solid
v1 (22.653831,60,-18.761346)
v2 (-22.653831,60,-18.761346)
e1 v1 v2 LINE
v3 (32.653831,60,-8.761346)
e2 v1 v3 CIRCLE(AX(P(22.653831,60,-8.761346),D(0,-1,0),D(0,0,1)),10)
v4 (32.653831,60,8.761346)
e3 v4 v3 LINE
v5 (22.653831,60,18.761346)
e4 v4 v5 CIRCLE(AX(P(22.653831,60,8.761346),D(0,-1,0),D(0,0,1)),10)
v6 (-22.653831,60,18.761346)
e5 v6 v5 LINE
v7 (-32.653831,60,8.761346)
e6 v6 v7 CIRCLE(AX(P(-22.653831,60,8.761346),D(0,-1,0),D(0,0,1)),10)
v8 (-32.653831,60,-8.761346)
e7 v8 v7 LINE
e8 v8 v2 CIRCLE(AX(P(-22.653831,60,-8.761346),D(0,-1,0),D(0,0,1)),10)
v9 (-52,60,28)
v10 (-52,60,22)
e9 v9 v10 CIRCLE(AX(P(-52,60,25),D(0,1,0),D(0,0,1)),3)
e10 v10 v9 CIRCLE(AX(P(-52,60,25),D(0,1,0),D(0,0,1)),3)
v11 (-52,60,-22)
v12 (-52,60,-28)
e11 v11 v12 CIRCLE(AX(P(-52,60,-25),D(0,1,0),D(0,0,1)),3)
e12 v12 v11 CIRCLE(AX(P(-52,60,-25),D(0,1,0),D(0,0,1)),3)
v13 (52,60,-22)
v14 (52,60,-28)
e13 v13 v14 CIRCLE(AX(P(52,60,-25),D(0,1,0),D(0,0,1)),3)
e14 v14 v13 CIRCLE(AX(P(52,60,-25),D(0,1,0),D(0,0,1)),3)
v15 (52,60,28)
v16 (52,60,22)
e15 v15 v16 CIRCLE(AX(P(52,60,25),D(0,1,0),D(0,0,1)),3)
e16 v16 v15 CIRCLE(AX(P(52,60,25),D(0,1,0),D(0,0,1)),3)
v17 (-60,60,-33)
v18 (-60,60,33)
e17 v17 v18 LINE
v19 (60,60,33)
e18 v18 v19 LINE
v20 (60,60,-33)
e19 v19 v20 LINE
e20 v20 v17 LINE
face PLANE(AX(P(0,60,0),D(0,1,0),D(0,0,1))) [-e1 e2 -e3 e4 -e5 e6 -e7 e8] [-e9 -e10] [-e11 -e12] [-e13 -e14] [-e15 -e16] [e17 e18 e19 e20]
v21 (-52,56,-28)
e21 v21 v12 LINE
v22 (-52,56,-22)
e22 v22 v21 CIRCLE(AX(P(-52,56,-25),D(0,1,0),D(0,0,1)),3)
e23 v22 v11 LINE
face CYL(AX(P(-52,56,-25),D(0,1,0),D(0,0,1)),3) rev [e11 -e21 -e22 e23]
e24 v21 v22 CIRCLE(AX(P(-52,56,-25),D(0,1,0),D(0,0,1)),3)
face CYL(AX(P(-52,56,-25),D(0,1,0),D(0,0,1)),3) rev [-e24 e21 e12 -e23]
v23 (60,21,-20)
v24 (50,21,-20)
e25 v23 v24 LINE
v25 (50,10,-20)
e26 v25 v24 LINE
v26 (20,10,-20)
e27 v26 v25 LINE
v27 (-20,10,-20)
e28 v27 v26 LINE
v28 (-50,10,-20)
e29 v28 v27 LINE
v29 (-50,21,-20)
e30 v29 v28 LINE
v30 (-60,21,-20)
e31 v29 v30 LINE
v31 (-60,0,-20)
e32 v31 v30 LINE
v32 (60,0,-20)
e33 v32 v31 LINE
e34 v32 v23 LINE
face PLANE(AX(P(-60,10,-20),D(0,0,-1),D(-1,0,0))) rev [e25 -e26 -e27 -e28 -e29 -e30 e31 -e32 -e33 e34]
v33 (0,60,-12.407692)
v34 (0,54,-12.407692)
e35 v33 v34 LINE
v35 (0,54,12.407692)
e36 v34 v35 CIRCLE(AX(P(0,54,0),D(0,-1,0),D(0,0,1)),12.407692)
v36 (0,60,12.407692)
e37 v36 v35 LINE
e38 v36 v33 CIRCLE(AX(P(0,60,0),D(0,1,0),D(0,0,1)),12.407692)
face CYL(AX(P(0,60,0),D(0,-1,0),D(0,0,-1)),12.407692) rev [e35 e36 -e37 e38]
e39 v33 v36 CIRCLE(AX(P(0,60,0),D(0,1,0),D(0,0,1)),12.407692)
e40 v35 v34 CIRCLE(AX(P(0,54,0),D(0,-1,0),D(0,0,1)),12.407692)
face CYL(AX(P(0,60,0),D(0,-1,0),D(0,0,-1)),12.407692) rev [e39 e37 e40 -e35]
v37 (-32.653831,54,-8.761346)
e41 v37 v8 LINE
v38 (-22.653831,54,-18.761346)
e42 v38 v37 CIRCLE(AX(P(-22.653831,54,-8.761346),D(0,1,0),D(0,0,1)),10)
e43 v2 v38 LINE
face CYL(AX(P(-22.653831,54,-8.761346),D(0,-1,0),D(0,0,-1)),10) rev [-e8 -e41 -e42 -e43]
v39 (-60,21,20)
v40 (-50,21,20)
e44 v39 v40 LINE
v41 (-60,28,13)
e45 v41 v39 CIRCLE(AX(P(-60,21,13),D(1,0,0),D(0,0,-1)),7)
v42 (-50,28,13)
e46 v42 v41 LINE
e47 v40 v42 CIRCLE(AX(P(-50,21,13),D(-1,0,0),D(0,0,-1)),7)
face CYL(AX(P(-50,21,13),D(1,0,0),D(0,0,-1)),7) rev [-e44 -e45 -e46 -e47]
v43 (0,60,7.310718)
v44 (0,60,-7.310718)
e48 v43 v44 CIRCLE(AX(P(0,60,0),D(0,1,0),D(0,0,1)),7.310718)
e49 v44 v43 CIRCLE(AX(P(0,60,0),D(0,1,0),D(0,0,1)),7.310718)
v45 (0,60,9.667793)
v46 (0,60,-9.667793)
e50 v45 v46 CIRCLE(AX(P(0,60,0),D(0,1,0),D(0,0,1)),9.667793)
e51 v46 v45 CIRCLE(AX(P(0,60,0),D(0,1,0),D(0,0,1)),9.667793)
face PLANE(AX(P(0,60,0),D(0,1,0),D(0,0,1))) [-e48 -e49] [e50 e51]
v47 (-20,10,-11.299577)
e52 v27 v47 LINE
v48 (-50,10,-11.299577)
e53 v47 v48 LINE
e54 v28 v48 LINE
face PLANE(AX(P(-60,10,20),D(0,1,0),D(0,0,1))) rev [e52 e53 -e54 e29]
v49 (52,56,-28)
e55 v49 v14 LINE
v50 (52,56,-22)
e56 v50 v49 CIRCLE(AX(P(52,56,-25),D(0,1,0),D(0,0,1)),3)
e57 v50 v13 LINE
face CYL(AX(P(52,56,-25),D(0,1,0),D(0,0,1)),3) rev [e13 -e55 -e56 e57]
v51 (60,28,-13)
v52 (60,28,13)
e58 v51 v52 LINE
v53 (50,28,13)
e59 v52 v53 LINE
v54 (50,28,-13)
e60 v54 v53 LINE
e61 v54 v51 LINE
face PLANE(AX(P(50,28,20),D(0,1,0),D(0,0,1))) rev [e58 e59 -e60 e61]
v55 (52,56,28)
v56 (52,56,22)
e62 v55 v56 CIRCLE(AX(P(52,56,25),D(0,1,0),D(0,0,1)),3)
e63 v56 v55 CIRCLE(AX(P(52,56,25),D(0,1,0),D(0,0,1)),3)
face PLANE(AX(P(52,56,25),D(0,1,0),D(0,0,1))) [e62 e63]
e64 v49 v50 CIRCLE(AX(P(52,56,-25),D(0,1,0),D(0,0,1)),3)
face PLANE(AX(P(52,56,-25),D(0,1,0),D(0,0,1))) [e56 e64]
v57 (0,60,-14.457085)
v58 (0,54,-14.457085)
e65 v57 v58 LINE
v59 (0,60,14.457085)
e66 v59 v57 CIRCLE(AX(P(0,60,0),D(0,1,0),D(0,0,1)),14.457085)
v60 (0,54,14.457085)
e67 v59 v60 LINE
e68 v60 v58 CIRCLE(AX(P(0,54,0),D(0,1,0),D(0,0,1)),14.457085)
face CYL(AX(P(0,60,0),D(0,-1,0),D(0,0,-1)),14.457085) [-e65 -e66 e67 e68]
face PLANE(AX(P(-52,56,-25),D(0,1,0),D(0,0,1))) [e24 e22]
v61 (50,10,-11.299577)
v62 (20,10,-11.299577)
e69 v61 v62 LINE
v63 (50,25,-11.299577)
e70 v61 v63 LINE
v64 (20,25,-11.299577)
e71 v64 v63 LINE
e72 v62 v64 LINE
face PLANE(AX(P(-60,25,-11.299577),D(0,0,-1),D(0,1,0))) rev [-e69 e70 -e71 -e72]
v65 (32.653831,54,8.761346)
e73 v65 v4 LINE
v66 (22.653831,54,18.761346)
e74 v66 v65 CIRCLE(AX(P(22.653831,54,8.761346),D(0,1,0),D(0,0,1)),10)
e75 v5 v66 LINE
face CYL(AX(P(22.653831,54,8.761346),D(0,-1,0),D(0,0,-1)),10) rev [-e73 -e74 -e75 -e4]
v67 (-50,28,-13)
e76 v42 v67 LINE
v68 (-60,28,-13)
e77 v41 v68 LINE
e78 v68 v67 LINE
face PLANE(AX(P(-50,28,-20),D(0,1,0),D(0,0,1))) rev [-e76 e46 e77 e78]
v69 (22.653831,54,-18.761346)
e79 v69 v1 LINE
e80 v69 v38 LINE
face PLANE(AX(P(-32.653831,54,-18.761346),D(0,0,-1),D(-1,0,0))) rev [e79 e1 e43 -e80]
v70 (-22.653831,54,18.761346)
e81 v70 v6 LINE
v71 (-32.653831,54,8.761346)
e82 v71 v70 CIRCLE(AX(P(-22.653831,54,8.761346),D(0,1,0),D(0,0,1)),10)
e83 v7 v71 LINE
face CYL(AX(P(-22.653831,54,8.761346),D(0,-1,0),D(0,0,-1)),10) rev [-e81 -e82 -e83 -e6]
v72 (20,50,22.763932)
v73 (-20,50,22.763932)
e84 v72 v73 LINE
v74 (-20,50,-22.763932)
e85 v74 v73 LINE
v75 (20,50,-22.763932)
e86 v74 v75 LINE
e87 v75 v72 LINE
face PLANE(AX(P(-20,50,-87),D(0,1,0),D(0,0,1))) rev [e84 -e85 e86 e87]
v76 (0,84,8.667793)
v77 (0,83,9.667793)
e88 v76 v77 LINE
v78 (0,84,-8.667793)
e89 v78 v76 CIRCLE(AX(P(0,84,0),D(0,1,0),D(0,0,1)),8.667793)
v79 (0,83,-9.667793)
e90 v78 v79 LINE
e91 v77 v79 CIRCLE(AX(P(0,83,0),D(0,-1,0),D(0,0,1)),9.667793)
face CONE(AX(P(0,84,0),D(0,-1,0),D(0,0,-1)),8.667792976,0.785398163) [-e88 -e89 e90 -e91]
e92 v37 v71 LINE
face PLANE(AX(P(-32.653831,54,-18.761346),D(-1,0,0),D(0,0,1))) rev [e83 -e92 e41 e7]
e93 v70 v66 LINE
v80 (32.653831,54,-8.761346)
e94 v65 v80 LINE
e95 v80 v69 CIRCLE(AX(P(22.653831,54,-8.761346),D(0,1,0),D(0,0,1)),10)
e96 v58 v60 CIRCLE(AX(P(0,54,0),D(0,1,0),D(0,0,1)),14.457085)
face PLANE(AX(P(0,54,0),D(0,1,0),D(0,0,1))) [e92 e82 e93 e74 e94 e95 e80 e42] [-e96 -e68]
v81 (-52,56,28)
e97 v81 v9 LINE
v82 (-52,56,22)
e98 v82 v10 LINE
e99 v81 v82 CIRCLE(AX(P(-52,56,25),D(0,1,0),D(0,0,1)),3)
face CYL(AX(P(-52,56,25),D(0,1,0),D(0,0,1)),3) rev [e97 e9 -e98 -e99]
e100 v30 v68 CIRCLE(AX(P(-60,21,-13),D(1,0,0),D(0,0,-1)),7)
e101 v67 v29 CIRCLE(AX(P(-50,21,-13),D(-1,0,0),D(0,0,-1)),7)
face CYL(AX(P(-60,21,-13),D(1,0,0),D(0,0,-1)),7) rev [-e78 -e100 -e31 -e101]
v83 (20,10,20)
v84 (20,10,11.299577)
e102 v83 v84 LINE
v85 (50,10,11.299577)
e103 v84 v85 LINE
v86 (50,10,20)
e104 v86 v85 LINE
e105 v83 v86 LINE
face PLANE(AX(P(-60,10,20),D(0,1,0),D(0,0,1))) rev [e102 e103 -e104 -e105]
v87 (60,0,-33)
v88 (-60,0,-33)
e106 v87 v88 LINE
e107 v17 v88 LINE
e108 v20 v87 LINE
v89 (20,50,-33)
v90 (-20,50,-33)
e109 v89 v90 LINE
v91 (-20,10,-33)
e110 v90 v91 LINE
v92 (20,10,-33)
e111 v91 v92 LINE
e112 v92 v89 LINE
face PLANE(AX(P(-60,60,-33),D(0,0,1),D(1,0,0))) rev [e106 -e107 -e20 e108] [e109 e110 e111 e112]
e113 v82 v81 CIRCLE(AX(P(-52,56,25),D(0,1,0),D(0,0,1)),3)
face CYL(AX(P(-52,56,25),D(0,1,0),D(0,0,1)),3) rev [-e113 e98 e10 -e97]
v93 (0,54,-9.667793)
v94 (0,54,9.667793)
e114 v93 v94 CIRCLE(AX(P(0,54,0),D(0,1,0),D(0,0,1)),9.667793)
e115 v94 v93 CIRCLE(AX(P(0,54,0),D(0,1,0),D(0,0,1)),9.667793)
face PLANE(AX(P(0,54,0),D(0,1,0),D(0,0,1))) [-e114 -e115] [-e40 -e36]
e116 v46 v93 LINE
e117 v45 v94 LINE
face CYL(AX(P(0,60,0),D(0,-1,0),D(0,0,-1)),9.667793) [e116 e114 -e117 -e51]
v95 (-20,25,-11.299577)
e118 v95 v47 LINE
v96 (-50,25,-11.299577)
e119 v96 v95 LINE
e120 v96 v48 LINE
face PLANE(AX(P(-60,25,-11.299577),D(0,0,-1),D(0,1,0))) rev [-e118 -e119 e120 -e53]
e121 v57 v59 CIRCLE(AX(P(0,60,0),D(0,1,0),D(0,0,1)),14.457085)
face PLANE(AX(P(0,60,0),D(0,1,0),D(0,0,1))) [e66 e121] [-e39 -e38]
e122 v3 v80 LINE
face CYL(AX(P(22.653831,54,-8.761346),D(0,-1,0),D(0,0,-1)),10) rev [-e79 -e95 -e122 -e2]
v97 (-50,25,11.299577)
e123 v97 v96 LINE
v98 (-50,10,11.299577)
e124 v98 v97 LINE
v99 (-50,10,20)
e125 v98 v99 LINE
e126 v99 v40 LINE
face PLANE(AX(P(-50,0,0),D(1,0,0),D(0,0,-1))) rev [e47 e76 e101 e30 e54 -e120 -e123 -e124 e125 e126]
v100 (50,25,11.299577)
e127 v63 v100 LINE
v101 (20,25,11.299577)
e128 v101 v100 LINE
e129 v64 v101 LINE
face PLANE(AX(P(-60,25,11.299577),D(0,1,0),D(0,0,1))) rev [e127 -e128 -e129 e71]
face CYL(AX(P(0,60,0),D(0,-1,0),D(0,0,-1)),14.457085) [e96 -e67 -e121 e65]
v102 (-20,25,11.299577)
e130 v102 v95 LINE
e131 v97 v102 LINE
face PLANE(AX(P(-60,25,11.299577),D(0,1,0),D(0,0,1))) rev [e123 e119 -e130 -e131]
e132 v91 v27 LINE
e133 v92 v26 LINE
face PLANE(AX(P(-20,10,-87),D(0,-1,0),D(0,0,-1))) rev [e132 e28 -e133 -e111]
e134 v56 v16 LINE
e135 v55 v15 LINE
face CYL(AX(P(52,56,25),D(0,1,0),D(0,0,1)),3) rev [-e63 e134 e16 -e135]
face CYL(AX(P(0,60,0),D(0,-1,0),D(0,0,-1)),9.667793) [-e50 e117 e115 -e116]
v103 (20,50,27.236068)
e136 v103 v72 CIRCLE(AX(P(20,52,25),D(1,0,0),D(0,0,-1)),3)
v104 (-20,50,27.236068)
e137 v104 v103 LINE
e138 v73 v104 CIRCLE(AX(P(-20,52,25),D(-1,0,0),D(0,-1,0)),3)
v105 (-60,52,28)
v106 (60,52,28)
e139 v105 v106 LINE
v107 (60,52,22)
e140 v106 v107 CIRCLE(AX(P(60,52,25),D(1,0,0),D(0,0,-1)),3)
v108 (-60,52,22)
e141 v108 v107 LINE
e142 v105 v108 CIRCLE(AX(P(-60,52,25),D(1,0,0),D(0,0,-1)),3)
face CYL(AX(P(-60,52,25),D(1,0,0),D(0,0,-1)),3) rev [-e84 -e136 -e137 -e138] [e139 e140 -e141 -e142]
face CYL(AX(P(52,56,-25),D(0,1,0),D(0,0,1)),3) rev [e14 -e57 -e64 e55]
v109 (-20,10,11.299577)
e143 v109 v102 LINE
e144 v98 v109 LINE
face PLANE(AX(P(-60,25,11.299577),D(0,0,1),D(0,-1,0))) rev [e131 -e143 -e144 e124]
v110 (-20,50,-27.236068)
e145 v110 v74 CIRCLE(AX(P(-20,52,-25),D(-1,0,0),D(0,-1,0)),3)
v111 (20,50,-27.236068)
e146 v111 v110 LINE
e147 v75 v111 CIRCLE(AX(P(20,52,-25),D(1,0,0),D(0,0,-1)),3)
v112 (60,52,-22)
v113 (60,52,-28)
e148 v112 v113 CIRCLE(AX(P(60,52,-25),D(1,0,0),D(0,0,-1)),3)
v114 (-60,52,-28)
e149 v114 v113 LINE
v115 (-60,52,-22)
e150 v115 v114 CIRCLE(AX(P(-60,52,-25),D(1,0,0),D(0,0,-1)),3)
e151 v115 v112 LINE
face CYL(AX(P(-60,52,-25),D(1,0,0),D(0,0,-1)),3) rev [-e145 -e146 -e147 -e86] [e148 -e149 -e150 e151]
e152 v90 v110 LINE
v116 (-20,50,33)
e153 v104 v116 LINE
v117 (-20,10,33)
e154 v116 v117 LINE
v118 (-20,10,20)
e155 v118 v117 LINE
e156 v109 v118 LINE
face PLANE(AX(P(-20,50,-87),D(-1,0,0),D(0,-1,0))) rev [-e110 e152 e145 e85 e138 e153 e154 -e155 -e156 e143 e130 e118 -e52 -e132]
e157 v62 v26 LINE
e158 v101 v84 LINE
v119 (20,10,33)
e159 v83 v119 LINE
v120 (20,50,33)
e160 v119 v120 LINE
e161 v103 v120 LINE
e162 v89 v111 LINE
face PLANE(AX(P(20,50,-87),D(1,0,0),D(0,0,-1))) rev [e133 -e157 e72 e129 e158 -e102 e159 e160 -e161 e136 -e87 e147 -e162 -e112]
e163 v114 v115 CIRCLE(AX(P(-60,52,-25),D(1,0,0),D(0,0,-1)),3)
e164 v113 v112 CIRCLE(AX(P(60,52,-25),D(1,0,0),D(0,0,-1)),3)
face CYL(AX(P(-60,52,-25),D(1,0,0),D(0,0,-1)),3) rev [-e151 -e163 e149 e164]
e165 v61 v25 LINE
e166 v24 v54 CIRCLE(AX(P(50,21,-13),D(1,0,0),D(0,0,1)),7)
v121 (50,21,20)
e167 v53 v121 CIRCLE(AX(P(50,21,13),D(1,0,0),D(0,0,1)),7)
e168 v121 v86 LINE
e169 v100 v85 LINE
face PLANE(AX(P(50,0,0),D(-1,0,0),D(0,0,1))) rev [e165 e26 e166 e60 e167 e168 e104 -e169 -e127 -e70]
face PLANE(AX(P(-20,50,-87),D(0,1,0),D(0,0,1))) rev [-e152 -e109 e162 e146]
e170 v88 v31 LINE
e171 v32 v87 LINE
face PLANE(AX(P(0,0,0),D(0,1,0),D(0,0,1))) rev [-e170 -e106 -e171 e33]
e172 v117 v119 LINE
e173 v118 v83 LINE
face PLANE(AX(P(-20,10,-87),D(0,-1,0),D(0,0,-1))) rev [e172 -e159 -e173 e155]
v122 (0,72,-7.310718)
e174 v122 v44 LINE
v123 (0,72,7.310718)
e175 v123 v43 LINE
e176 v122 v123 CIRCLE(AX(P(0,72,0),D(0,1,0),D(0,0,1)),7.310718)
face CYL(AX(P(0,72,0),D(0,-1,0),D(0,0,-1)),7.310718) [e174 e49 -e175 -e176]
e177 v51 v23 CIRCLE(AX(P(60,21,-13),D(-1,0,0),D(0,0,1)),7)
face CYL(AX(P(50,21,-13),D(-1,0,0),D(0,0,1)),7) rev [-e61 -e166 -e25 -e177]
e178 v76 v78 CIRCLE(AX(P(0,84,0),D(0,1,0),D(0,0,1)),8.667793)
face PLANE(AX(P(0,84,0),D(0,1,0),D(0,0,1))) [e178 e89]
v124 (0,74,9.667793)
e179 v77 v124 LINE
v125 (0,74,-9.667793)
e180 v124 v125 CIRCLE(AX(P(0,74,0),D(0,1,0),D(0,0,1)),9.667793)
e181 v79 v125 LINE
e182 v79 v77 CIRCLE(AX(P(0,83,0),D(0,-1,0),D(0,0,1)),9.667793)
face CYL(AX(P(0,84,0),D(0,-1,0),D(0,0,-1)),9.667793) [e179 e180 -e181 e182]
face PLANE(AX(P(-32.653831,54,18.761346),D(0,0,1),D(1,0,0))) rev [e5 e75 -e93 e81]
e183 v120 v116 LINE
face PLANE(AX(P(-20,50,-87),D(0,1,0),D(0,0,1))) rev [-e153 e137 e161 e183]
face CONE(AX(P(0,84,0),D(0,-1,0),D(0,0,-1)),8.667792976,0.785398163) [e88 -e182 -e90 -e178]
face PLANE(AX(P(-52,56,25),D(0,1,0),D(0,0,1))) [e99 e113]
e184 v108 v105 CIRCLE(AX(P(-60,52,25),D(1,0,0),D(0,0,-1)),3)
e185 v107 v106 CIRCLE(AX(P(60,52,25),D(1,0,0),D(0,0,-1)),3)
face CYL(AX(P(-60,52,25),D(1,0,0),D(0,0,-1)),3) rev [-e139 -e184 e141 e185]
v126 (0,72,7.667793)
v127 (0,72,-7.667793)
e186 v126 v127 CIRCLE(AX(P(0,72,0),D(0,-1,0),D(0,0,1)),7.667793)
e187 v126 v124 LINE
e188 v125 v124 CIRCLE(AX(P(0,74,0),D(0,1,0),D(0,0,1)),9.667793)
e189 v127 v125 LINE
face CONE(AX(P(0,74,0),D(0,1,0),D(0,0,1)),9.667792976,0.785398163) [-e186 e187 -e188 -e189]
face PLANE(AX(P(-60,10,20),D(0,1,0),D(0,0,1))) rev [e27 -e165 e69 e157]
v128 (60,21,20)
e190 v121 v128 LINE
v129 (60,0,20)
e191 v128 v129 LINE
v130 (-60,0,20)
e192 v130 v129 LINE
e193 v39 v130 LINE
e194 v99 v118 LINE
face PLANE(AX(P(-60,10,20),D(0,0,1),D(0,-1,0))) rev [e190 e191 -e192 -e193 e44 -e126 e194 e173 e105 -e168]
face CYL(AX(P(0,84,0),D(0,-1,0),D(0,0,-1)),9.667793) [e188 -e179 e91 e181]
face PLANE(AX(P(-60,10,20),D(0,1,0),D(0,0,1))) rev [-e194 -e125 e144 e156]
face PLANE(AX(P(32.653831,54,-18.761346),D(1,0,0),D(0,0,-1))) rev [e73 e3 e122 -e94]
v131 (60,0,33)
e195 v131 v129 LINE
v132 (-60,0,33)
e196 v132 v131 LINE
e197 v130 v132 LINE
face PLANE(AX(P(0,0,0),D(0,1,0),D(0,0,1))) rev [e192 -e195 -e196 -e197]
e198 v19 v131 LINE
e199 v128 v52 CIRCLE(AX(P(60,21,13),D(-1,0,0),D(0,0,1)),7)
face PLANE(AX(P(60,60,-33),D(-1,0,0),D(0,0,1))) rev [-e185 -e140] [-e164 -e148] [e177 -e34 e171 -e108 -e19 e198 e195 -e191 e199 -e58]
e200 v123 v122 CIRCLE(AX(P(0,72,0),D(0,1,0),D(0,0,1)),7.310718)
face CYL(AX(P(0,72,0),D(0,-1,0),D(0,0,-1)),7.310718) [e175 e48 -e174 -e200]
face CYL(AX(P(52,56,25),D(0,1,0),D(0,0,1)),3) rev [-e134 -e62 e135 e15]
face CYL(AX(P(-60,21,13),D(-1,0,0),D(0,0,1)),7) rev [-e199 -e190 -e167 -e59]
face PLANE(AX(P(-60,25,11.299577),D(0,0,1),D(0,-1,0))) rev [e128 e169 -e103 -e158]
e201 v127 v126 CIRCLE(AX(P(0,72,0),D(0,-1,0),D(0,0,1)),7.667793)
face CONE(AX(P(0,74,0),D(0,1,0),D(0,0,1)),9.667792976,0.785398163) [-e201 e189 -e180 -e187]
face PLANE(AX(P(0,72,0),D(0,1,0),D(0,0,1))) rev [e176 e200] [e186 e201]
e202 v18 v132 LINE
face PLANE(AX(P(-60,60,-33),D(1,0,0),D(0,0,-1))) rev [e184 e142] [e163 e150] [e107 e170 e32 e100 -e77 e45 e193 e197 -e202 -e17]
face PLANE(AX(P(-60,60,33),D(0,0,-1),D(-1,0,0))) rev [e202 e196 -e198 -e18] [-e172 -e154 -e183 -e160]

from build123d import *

# Parameters (mm, degrees)
SKETCH1_W           = 120
SKETCH1_H           = 66
BOSS_EXTRUDE1_DEPTH = 60
SKETCH3_W           = 40
SKETCH3_H           = 20
CUT_EXTRUDE1_DEPTH  = 120
SKETCH4_W           = 40
SKETCH4_H           = 40
CUT_EXTRUDE2_DEPTH  = 120
SKETCH5_W           = 22.599154532
SKETCH5_H           = 30
CUT_EXTRUDE3_DEPTH  = 120
SKETCH6_R           = 3
CUT_EXTRUDE4_DEPTH  = 120
SKETCH7_W           = 40
SKETCH7_H           = 18
CUT_EXTRUDE5_DEPTH  = 10
SKETCH8_W           = 40
SKETCH8_H           = 18
CUT_EXTRUDE6_DEPTH  = 10
SKETCH9_W           = 65.307661508
SKETCH9_H           = 37.522692198
CUT_EXTRUDE7_DEPTH  = 6
FILLET1_R           = 10
SKETCH10_R          = 3
CUT_EXTRUDE8_DEPTH  = 4
FILLET2_R           = 7
SKETCH11_R          = 14.45708456
SKETCH11_R_2        = 12.407691548
BOSS_EXTRUDE2_DEPTH = 6
SKETCH12_R          = 9.667792976
BOSS_EXTRUDE3_DEPTH = 6
SKETCH13_R          = 7.310717913
BOSS_EXTRUDE4_DEPTH = 12
SKETCH14_R          = 9.667792976
BOSS_EXTRUDE5_DEPTH = 12
CHAMFER1_SIZE       = 2
CHAMFER2_SIZE       = 1


with BuildPart() as part:
    # Sketch1 → Boss-Extrude1 (new body)
    with BuildSketch(Plane(origin=(0, 0, 0), x_dir=(1, 0, 0), z_dir=(0, 1, 0))):
        Rectangle(SKETCH1_W, SKETCH1_H)
    extrude(amount=BOSS_EXTRUDE1_DEPTH)

    # Sketch3 → Cut-Extrude1 (cut)
    with BuildSketch(Plane(origin=(60, 0, 0), x_dir=(0, 0, -1), z_dir=(1, 0, 0))):
        Rectangle(SKETCH3_W, SKETCH3_H)
    extrude(amount=-CUT_EXTRUDE1_DEPTH, mode=Mode.SUBTRACT)

    # Sketch4 → Cut-Extrude2 (cut)
    with BuildSketch(Plane.XY.offset(33)):
        with Locations((0, 30)):
            Rectangle(SKETCH4_W, SKETCH4_H)
    extrude(amount=-CUT_EXTRUDE2_DEPTH, mode=Mode.SUBTRACT)

    # Sketch5 → Cut-Extrude3 (cut)
    with BuildSketch(Plane(origin=(60, 0, 0), x_dir=(0, 0, -1), z_dir=(1, 0, 0))):
        with Locations((0, 10)):
            Rectangle(SKETCH5_W, SKETCH5_H)
    extrude(amount=-CUT_EXTRUDE3_DEPTH, mode=Mode.SUBTRACT)

    # Sketch6 → Cut-Extrude4 (cut)
    with BuildSketch(Plane(origin=(60, 0, 0), x_dir=(0, 0, -1), z_dir=(1, 0, 0))):
        with Locations((-25, 52)):
            Circle(SKETCH6_R)
        with Locations((25, 52)):
            Circle(SKETCH6_R)
    extrude(amount=-CUT_EXTRUDE4_DEPTH, mode=Mode.SUBTRACT)

    # Sketch7 → Cut-Extrude5 (cut)
    with BuildSketch(Plane(origin=(60, 0, 0), x_dir=(0, 0, -1), z_dir=(1, 0, 0))):
        with Locations((0, 19)):
            Rectangle(SKETCH7_W, SKETCH7_H)
    extrude(amount=-CUT_EXTRUDE5_DEPTH, mode=Mode.SUBTRACT)

    # Sketch8 → Cut-Extrude6 (cut)
    with BuildSketch(Plane.ZY.offset(60)):
        with Locations((0, 19)):
            Rectangle(SKETCH8_W, SKETCH8_H)
    extrude(amount=-CUT_EXTRUDE6_DEPTH, mode=Mode.SUBTRACT)

    # Sketch9 → Cut-Extrude7 (cut)
    with BuildSketch(Plane(origin=(0, 60, 0), x_dir=(1, 0, 0), z_dir=(0, 1, 0))):
        Rectangle(SKETCH9_W, SKETCH9_H)
    extrude(amount=-CUT_EXTRUDE7_DEPTH, mode=Mode.SUBTRACT)

    # Fillet1
    fillet1_edges = [part.edges().sort_by_distance(p)[0] for p in [
        (32.653830754, 57, -18.761346099),
        (32.653830754, 57, 18.761346099),
        (-32.653830754, 57, 18.761346099),
        (-32.653830754, 57, -18.761346099),
    ]]
    fillet(fillet1_edges, radius=FILLET1_R)

    # Sketch10 → Cut-Extrude8 (cut)
    with BuildSketch(Plane(origin=(0, 60, 0), x_dir=(1, 0, 0), z_dir=(0, 1, 0))):
        with Locations(Location((-52, 25, 0), (0, 0, 270))):
            Circle(SKETCH10_R)
        with Locations(Location((52, 25, 0), (0, 0, 270))):
            Circle(SKETCH10_R)
        with Locations(Location((-52, -25, 0), (0, 0, 270))):
            Circle(SKETCH10_R)
        with Locations(Location((52, -25, 0), (0, 0, 270))):
            Circle(SKETCH10_R)
    extrude(amount=-CUT_EXTRUDE8_DEPTH, mode=Mode.SUBTRACT)

    # Fillet2
    fillet2_edges = [part.edges().sort_by_distance(p)[0] for p in [
        (55, 28, 20),
        (55, 28, -20),
        (-55, 28, -20),
        (-55, 28, 20),
    ]]
    fillet(fillet2_edges, radius=FILLET2_R)

    # Sketch11 → Boss-Extrude2 (add)
    with BuildSketch(Plane(origin=(0, 54, 0), x_dir=(1, 0, 0), z_dir=(0, 1, 0))):
        with Locations(Location((0, 0, 0), (0, 0, 270))):
            Circle(SKETCH11_R)
        with Locations(Location((0, 0, 0), (0, 0, 270))):
            Circle(SKETCH11_R_2, mode=Mode.SUBTRACT)
    extrude(amount=BOSS_EXTRUDE2_DEPTH)

    # Sketch12 → Boss-Extrude3 (add)
    with BuildSketch(Plane(origin=(0, 54, 0), x_dir=(1, 0, 0), z_dir=(0, 1, 0))):
        with Locations(Location((0, 0, 0), (0, 0, 270))):
            Circle(SKETCH12_R)
    extrude(amount=BOSS_EXTRUDE3_DEPTH)

    # Sketch13 → Boss-Extrude4 (add)
    with BuildSketch(Plane(origin=(0, 60, 0), x_dir=(1, 0, 0), z_dir=(0, 1, 0))):
        with Locations(Location((0, 0, 0), (0, 0, 270))):
            Circle(SKETCH13_R)
    extrude(amount=BOSS_EXTRUDE4_DEPTH)

    # Sketch14 → Boss-Extrude5 (add)
    with BuildSketch(Plane(origin=(0, 72, 0), x_dir=(1, 0, 0), z_dir=(0, 1, 0))):
        with Locations(Location((0, 0, 0), (0, 0, 270))):
            Circle(SKETCH14_R)
    extrude(amount=BOSS_EXTRUDE5_DEPTH)

    # Chamfer1
    chamfer1_edges = [part.edges().sort_by_distance(p)[0] for p in [
        (0, 72, -9.667792976),
    ]]
    chamfer(chamfer1_edges, length=CHAMFER1_SIZE)

    # Chamfer2
    chamfer2_edges = [part.edges().sort_by_distance(p)[0] for p in [
        (0, 84, -9.667792976),
    ]]
    chamfer(chamfer2_edges, length=CHAMFER2_SIZE)


solid = part.part
